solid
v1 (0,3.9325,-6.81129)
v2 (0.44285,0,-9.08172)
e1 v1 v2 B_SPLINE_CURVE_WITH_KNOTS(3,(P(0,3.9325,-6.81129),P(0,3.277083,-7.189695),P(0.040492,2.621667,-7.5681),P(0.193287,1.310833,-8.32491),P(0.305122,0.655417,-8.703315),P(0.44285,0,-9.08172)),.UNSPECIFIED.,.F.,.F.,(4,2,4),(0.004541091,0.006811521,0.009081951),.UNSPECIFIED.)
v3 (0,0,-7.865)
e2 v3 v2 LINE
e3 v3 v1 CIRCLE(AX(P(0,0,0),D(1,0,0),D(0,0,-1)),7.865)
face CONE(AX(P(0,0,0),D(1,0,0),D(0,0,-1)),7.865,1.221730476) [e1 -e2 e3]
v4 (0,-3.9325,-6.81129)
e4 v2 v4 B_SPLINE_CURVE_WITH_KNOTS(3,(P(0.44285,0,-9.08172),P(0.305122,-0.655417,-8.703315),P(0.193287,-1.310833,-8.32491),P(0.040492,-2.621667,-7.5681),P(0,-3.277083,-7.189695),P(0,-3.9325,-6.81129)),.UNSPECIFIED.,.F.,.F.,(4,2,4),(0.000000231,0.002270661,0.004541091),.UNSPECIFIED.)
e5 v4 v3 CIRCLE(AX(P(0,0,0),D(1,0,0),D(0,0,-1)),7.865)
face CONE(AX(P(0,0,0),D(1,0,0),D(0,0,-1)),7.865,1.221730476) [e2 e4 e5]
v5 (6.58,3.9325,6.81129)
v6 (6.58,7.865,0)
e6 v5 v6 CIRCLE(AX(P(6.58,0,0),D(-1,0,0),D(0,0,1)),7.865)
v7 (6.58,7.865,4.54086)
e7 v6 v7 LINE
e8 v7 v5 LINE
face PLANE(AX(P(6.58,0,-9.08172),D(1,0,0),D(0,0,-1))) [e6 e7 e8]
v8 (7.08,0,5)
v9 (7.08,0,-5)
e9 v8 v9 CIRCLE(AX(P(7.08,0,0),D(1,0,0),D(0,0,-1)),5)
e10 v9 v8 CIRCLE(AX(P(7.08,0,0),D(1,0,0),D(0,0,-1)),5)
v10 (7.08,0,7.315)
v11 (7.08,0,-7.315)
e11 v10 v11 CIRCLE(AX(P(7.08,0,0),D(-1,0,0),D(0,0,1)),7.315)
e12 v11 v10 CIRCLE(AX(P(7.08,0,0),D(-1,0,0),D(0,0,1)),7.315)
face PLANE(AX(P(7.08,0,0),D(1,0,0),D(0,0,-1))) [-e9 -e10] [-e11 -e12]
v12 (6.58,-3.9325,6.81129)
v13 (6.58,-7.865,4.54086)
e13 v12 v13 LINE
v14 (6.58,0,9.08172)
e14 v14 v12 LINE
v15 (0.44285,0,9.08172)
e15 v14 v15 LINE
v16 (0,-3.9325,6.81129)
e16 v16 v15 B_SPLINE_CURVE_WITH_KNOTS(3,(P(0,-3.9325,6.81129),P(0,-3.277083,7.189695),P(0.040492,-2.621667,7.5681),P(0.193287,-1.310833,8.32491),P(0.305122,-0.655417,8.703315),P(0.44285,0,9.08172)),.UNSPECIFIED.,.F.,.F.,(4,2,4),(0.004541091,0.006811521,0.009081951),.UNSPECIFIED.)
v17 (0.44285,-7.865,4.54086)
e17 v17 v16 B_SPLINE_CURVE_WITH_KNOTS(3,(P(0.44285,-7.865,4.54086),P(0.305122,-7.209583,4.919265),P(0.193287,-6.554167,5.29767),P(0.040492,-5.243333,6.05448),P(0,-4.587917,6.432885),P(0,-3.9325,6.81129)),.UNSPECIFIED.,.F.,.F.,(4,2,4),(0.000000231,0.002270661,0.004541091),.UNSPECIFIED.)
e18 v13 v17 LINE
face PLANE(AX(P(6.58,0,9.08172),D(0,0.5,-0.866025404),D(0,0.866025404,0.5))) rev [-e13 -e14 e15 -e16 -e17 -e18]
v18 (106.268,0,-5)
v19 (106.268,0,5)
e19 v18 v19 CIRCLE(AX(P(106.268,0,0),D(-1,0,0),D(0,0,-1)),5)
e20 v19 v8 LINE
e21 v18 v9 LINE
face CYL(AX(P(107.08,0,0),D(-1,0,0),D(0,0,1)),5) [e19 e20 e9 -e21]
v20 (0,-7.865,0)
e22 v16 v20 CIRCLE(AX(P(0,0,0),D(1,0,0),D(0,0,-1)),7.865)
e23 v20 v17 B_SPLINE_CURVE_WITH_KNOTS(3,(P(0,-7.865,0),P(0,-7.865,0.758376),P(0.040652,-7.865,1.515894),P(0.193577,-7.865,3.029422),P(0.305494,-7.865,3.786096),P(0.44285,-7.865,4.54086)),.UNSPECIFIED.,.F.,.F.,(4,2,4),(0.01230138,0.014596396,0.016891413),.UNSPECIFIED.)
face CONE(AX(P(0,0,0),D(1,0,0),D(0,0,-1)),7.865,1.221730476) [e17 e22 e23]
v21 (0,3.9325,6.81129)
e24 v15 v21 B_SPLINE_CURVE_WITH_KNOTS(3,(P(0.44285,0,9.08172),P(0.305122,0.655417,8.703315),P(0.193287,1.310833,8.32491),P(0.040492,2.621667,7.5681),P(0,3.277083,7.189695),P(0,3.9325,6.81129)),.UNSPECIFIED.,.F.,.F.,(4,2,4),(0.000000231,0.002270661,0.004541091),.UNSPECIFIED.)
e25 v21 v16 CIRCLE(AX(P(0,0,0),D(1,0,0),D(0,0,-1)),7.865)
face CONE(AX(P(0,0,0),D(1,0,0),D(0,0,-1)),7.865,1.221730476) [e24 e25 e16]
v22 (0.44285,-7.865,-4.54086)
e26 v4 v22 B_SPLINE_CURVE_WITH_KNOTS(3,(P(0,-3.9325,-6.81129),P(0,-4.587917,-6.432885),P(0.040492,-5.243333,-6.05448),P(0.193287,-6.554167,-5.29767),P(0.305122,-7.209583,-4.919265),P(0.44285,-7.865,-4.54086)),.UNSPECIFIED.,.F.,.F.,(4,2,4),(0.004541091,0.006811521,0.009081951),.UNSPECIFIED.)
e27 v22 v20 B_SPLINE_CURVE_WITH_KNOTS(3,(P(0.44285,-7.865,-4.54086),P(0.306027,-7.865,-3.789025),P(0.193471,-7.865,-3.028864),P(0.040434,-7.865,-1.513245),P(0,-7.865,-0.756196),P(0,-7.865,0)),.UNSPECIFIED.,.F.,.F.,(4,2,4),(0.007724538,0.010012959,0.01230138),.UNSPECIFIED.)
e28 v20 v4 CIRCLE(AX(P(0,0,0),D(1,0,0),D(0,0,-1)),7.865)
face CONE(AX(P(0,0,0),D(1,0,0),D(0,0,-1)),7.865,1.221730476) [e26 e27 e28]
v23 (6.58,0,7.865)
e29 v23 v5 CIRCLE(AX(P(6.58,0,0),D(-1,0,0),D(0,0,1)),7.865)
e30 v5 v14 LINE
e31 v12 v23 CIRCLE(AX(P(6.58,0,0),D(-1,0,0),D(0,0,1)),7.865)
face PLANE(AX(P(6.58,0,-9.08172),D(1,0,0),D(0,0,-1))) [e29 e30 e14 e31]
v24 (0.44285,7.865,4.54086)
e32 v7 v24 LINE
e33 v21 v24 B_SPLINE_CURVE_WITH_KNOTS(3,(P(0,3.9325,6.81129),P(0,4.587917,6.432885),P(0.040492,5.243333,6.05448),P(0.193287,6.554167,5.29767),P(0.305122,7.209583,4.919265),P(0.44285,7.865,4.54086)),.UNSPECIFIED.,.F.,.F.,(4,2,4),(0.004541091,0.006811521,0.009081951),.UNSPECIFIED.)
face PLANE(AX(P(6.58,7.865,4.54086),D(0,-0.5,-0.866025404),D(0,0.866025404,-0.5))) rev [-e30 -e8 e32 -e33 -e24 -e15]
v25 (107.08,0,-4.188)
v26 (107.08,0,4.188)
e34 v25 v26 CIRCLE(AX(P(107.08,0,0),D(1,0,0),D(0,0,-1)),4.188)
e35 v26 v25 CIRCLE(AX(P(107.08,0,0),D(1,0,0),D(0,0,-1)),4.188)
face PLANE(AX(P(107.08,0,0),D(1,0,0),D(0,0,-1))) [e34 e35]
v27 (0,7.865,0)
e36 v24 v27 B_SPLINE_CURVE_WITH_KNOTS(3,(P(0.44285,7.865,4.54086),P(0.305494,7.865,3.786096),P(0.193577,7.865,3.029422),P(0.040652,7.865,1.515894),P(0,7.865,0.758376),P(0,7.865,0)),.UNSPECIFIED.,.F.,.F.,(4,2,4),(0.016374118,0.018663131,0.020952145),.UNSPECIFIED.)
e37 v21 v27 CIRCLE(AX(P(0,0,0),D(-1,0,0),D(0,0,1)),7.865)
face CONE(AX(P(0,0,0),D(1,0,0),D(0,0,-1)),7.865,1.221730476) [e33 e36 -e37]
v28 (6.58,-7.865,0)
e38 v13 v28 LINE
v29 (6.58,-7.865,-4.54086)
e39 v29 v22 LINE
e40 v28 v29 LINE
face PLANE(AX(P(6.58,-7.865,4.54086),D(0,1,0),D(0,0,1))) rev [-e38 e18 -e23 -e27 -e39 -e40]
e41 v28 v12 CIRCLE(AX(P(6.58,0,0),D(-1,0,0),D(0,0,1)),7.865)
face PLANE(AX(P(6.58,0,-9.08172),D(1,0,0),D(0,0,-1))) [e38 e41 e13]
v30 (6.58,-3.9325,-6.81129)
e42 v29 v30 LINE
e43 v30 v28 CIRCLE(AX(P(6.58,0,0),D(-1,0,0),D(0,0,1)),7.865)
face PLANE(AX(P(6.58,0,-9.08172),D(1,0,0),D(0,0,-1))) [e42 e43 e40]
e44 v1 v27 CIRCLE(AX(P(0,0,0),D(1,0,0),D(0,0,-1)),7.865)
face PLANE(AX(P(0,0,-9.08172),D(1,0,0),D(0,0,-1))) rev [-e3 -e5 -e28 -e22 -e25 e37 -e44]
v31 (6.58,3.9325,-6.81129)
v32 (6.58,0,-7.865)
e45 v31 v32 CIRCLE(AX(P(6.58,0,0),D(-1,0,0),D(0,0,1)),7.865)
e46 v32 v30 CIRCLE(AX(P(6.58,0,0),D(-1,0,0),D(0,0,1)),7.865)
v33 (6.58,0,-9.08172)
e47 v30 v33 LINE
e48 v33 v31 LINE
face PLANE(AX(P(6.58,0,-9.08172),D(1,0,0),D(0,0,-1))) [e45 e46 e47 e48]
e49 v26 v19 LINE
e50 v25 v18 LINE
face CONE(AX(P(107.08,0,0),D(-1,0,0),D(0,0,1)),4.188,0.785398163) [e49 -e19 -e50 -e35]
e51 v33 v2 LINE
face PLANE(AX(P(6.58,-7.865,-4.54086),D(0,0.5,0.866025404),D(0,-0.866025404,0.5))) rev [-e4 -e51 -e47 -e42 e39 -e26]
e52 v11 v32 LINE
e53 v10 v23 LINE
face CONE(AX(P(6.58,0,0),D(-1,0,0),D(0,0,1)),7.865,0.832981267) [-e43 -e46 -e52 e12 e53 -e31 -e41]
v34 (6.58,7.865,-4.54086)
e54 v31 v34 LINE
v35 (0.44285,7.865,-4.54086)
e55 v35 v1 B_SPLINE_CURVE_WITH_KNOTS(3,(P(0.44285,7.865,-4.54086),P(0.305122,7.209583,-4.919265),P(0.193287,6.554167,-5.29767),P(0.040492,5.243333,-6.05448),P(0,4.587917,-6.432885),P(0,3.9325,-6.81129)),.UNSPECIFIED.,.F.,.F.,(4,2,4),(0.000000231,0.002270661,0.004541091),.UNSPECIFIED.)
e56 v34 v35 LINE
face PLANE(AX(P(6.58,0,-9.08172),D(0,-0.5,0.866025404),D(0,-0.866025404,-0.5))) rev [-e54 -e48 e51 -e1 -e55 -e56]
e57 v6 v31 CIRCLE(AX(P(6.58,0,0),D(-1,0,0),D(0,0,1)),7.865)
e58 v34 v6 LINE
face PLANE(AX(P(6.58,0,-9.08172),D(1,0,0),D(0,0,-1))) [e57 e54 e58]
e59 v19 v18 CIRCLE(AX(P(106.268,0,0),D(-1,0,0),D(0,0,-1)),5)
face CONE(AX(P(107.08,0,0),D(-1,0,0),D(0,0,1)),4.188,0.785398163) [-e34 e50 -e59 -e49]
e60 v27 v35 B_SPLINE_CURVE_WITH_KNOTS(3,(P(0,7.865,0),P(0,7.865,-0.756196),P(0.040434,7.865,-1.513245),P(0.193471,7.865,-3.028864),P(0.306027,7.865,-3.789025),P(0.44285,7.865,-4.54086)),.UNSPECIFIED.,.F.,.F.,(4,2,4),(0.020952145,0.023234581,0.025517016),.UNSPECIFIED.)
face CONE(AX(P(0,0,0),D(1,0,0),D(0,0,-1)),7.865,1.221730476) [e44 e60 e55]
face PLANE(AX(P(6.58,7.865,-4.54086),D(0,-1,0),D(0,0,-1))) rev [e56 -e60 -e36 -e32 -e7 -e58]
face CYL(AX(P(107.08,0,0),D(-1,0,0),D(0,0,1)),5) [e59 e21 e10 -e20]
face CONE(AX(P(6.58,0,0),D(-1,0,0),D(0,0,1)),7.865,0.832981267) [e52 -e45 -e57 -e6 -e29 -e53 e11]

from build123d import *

# Parameters (mm, degrees)
BASEHEAD_DEPTH = 6.58
SKETCH3_R      = 5
BASEBODY_DEPTH = 100
CHAMFER1_SIZE  = 0.812


with BuildPart() as part:
    # Sketch-BaseHead → BaseHead (new body)
    with BuildSketch(Plane(origin=(0, 0, 0), x_dir=(0, 0, -1), z_dir=(1, 0, 0))):
        Polygon((9.081719734, 0), (4.540859867, 7.865), (-4.540859867, 7.865), (-9.081719734, 0), (-4.540859867, -7.865), (4.540859867, -7.865), align=None)
    extrude(amount=BASEHEAD_DEPTH)

    # Sketch4 → HeadChamfer (revolve, cut)
    with BuildSketch(Plane(origin=(-0.264637255, 0, 5.916896391), x_dir=(0, 0, -1), z_dir=(0, 1, 0))):
        Polygon((14.998616125, -0.264637255), (13.781896391, -0.264637255), (14.998616125, -0.707487022), align=None)
    revolve(axis=Axis((-4.001564945, 0, 0), (1, 0, 0)), mode=Mode.SUBTRACT)

    # Sketch1 → Revolve1 (revolve)
    with BuildSketch(Plane.XY, mode=Mode.PRIVATE) as revolve1_sk:
        Polygon((6.58, 0), (7.08, 0), (7.08, -7.315), (6.58, -7.865), align=None)
    revolve(revolve1_sk.sketch.rotate(Axis((-4.001564945, 0, 0), (1, 0, 0)), 270), axis=Axis((-4.001564945, 0, 0), (1, 0, 0)))

    # Sketch3 → BaseBody (add)
    with BuildSketch(Plane(origin=(7.08, 0, 0), x_dir=(0, 0, -1), z_dir=(1, 0, 0))):
        Circle(SKETCH3_R)
    extrude(amount=BASEBODY_DEPTH)

    # Chamfer1
    chamfer1_edges = [part.edges().sort_by_distance(p)[0] for p in [
        (107.08, 0, 5),
    ]]
    chamfer(chamfer1_edges, length=CHAMFER1_SIZE)


solid = part.part
